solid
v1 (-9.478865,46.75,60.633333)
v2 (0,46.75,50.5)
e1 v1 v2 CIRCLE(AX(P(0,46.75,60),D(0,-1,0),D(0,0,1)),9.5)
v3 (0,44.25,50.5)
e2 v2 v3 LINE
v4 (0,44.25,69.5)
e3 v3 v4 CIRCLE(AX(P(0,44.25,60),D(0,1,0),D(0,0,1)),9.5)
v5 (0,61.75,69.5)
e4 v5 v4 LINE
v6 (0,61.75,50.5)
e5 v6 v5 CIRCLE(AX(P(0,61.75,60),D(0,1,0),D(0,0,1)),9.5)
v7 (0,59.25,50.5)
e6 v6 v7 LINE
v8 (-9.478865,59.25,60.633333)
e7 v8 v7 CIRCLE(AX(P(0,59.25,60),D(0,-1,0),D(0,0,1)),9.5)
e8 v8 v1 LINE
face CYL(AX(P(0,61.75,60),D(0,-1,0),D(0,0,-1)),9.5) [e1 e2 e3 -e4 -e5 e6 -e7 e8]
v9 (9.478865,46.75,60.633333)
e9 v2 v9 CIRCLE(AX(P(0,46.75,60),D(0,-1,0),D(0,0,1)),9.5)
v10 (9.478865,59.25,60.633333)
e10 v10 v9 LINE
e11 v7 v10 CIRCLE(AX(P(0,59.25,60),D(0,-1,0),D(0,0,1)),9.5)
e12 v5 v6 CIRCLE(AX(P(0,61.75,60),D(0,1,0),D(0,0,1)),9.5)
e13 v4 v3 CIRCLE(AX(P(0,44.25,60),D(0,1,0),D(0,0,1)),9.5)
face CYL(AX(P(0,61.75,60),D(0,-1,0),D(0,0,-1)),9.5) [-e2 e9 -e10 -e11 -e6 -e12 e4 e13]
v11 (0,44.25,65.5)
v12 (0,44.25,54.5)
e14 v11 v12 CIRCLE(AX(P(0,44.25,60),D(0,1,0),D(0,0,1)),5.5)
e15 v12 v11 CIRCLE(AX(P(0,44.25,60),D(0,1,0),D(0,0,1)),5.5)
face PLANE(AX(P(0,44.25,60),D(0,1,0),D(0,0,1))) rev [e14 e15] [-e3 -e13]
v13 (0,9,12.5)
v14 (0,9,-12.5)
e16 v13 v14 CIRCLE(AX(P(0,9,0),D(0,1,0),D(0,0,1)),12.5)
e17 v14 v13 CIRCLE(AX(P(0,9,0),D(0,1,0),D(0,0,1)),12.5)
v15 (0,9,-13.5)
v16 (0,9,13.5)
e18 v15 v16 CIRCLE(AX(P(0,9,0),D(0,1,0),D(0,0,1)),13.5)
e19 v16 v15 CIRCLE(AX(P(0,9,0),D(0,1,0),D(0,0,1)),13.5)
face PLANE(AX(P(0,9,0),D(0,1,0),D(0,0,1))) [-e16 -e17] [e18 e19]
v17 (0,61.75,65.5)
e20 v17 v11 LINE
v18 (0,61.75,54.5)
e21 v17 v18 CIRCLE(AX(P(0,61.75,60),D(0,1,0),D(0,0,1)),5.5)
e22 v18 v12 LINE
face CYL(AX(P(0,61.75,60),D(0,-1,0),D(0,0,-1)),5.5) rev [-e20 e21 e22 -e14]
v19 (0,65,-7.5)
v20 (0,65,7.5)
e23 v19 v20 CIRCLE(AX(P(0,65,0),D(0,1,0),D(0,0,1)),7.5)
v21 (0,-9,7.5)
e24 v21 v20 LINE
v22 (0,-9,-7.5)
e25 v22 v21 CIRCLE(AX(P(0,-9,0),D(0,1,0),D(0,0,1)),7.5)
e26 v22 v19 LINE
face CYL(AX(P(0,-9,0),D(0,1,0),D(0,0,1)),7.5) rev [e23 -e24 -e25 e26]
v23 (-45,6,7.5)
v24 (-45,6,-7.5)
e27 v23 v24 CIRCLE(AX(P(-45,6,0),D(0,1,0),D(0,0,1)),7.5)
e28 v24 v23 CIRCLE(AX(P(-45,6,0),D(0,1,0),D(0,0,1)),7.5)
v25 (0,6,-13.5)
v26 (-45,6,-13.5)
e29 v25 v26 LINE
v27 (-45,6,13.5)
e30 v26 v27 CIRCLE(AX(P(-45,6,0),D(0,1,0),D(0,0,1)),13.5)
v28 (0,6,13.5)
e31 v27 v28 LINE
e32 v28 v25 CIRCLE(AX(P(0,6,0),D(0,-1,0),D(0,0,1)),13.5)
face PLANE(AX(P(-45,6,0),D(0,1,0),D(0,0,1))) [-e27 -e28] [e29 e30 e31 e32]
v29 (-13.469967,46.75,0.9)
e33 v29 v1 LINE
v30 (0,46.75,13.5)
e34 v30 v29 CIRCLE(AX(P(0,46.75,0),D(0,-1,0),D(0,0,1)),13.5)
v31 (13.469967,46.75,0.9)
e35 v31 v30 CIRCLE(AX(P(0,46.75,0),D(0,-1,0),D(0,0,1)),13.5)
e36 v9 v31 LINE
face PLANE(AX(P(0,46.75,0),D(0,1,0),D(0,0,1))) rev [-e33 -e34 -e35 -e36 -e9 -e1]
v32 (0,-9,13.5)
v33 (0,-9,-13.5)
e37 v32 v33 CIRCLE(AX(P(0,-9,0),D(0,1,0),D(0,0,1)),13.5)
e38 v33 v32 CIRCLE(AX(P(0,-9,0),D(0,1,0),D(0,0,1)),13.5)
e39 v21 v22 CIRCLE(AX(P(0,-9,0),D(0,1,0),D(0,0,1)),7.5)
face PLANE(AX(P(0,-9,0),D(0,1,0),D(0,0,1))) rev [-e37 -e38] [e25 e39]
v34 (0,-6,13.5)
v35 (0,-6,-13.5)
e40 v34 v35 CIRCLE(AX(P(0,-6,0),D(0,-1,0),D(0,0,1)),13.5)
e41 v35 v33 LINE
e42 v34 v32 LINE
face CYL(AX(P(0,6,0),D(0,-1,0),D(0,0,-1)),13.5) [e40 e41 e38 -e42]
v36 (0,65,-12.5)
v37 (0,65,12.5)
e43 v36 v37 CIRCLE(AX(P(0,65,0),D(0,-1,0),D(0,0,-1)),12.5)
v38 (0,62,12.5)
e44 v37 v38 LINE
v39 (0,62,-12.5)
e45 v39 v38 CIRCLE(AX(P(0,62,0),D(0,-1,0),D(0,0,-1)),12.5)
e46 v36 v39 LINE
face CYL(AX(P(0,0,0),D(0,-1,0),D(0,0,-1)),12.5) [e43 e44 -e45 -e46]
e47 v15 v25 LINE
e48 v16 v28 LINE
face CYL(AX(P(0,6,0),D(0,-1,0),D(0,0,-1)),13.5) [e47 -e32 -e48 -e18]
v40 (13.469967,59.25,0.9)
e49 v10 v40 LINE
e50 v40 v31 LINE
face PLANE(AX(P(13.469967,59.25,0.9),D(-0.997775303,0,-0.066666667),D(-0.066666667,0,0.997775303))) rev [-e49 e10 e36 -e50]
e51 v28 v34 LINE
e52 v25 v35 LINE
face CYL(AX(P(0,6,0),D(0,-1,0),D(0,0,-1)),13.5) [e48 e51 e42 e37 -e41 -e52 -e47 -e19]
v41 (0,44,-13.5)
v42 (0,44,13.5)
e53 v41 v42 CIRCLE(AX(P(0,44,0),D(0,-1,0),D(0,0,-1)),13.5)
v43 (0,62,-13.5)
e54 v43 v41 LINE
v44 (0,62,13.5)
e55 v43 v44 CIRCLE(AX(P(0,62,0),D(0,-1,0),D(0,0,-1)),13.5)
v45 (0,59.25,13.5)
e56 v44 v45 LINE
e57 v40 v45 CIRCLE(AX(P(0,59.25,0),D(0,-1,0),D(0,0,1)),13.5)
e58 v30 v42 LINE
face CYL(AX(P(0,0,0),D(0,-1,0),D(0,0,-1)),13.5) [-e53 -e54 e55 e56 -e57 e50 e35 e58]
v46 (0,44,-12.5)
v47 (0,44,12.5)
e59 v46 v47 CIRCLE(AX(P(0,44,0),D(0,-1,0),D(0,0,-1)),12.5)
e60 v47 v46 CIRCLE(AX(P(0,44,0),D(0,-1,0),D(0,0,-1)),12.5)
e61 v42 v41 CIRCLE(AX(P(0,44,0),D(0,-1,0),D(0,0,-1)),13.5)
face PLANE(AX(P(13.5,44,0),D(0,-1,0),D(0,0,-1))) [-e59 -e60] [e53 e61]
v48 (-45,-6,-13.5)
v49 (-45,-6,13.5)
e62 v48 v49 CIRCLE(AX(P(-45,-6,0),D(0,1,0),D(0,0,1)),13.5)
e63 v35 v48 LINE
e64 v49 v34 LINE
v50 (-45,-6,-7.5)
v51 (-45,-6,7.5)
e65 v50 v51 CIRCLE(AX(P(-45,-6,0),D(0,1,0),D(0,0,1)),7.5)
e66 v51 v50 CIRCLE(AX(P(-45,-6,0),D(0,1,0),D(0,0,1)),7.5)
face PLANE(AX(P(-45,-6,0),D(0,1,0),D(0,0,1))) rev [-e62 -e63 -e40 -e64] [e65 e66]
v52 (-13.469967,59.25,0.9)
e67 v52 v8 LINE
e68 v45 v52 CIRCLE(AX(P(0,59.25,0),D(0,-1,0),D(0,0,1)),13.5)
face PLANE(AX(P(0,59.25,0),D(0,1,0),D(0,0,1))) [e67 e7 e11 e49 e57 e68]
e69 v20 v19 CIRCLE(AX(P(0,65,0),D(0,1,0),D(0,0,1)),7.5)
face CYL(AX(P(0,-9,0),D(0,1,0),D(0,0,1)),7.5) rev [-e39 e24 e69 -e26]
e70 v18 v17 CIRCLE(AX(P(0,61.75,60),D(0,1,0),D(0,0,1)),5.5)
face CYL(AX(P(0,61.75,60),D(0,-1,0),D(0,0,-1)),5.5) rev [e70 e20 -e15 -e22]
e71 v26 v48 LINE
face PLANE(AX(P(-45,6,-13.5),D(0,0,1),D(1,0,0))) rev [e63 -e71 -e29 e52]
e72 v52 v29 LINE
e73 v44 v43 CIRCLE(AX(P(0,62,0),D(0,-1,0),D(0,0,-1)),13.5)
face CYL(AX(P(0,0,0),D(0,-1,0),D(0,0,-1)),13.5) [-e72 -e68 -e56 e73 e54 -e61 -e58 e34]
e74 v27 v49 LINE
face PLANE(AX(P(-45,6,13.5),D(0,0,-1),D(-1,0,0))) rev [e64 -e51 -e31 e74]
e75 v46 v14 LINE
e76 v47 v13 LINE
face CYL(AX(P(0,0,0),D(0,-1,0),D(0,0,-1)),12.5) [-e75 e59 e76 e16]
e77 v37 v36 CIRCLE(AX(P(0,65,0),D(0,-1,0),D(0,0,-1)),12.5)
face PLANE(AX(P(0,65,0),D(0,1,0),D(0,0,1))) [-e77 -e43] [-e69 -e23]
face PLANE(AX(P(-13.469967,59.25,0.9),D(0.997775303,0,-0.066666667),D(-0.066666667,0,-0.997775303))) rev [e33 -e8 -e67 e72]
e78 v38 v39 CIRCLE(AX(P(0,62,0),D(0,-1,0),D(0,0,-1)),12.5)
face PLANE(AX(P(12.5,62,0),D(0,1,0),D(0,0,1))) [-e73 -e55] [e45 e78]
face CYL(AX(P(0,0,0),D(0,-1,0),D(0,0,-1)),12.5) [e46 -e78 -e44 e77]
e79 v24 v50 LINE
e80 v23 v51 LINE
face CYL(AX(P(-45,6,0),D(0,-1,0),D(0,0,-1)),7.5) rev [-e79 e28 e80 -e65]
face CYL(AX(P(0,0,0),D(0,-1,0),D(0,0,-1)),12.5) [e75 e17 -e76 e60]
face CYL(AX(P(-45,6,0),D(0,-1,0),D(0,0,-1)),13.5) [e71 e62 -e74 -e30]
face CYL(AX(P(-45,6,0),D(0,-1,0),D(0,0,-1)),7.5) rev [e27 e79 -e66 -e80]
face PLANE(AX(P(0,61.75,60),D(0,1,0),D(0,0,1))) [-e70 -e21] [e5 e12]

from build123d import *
from build123d.topology import SkipClean

# Parameters (mm, degrees)
LOWER_ARM_SKETCH_R  = 7.5
LOWER_ARM_DEPTH     = 6
HUB_BASE_SKETCH_R   = 13.5
HUB_BASE_BOSS_DEPTH = 9
PIVOT_BORE_SKETCH_R = 7.5
PIVOT_BORE_15_DEPTH = 96.291657557
END_BOSS_SKETCH_R   = 9.5
END_BOSS_SKETCH_R_2 = 5.5
END_BOSS_19_DEPTH   = 8.75
UPPER_ARM_DEPTH     = 6.25


with BuildPart() as part:
    # Lower Arm Sketch → Lower Arm (new, symmetric)
    with BuildSketch(Plane(origin=(0, 0, 0), x_dir=(1, 0, 0), z_dir=(0, 1, 0))):
        with BuildLine():
            Line((-45, 13.5), (0, 13.5))
            ThreePointArc((0, 13.5), (13.5, 0), (0, -13.5))
            Line((0, -13.5), (-45, -13.5))
            ThreePointArc((-45, -13.5), (-58.5, 0), (-45, 13.5))
        make_face()
        with Locations(Location((-45, 0, 0), (0, 0, 270))):
            Circle(LOWER_ARM_SKETCH_R, mode=Mode.SUBTRACT)
    extrude(amount=LOWER_ARM_DEPTH, both=True)

    # Hub Base Sketch → Hub Base Boss (add, symmetric)
    with SkipClean():  # the faces are left unmerged after this step: merging them gives an invalid solid
        with BuildSketch(Plane(origin=(0, 0, 0), x_dir=(1, 0, 0), z_dir=(0, 1, 0))):
            with Locations(Location((0, 0, 0), (0, 0, 270))):
                Circle(HUB_BASE_SKETCH_R)
        extrude(amount=HUB_BASE_BOSS_DEPTH, both=True)

    # Pivot Hub Profile → Pivot Hub (revolve)
    with SkipClean():  # the faces are left unmerged after this step: merging them gives an invalid solid
        with BuildSketch(Plane.XY, mode=Mode.PRIVATE) as pivot_hub_sk:
            Polygon((0, 0), (0, 65), (12.5, 65), (12.5, 62), (13.5, 62), (13.5, 44), (12.5, 44), (12.5, 0), align=None)
        revolve(pivot_hub_sk.sketch.rotate(Axis((0, 0, 0), (0, 1, 0)), 90), axis=Axis((0, 0, 0), (0, 1, 0)))

    # Pivot Bore Sketch → Pivot Bore Ø15 (cut, through all)
    with SkipClean():  # the faces are left unmerged after this step: merging them gives an invalid solid
        with BuildSketch(Plane(origin=(0, 65, 0), x_dir=(1, 0, 0), z_dir=(0, 1, 0))):
            with Locations(Location((0, 0, 0), (0, 0, 270))):
                Circle(PIVOT_BORE_SKETCH_R)
        extrude(amount=-PIVOT_BORE_15_DEPTH, mode=Mode.SUBTRACT)



with BuildPart() as body_2:
    # End Boss Sketch → End Boss Ø19 (new, symmetric)
    with BuildSketch(Plane(origin=(0, 53, 0), x_dir=(1, 0, 0), z_dir=(0, 1, 0))):
        with Locations(Location((0, -60, 0), (0, 0, 270))):
            Circle(END_BOSS_SKETCH_R)
        with Locations(Location((0, -60, 0), (0, 0, 270))):
            Circle(END_BOSS_SKETCH_R_2, mode=Mode.SUBTRACT)
    extrude(amount=END_BOSS_19_DEPTH, both=True)


with BuildPart() as part_1:
    with SkipClean():  # the faces are left unmerged after this step: merging them gives an invalid solid
        add(part.part)

        add(body_2.part)  # Upper Arm merges body 2
        # Upper Arm Sketch → Upper Arm (add, symmetric)
        with BuildSketch(Plane(origin=(0, 53, 0), x_dir=(1, 0, 0), z_dir=(0, 1, 0))):
            with BuildLine():
                Line((13.469966592, -0.9), (9.47886538, -60.633333333))
                ThreePointArc((9.47886538, -60.633333333), (0, -50.5), (-9.47886538, -60.633333333))
                Line((-9.47886538, -60.633333333), (-13.469966592, -0.9))
                ThreePointArc((-13.469966592, -0.9), (0, -13.5), (13.469966592, -0.9))
            make_face()
        extrude(amount=UPPER_ARM_DEPTH, both=True)


solid = part_1.part
